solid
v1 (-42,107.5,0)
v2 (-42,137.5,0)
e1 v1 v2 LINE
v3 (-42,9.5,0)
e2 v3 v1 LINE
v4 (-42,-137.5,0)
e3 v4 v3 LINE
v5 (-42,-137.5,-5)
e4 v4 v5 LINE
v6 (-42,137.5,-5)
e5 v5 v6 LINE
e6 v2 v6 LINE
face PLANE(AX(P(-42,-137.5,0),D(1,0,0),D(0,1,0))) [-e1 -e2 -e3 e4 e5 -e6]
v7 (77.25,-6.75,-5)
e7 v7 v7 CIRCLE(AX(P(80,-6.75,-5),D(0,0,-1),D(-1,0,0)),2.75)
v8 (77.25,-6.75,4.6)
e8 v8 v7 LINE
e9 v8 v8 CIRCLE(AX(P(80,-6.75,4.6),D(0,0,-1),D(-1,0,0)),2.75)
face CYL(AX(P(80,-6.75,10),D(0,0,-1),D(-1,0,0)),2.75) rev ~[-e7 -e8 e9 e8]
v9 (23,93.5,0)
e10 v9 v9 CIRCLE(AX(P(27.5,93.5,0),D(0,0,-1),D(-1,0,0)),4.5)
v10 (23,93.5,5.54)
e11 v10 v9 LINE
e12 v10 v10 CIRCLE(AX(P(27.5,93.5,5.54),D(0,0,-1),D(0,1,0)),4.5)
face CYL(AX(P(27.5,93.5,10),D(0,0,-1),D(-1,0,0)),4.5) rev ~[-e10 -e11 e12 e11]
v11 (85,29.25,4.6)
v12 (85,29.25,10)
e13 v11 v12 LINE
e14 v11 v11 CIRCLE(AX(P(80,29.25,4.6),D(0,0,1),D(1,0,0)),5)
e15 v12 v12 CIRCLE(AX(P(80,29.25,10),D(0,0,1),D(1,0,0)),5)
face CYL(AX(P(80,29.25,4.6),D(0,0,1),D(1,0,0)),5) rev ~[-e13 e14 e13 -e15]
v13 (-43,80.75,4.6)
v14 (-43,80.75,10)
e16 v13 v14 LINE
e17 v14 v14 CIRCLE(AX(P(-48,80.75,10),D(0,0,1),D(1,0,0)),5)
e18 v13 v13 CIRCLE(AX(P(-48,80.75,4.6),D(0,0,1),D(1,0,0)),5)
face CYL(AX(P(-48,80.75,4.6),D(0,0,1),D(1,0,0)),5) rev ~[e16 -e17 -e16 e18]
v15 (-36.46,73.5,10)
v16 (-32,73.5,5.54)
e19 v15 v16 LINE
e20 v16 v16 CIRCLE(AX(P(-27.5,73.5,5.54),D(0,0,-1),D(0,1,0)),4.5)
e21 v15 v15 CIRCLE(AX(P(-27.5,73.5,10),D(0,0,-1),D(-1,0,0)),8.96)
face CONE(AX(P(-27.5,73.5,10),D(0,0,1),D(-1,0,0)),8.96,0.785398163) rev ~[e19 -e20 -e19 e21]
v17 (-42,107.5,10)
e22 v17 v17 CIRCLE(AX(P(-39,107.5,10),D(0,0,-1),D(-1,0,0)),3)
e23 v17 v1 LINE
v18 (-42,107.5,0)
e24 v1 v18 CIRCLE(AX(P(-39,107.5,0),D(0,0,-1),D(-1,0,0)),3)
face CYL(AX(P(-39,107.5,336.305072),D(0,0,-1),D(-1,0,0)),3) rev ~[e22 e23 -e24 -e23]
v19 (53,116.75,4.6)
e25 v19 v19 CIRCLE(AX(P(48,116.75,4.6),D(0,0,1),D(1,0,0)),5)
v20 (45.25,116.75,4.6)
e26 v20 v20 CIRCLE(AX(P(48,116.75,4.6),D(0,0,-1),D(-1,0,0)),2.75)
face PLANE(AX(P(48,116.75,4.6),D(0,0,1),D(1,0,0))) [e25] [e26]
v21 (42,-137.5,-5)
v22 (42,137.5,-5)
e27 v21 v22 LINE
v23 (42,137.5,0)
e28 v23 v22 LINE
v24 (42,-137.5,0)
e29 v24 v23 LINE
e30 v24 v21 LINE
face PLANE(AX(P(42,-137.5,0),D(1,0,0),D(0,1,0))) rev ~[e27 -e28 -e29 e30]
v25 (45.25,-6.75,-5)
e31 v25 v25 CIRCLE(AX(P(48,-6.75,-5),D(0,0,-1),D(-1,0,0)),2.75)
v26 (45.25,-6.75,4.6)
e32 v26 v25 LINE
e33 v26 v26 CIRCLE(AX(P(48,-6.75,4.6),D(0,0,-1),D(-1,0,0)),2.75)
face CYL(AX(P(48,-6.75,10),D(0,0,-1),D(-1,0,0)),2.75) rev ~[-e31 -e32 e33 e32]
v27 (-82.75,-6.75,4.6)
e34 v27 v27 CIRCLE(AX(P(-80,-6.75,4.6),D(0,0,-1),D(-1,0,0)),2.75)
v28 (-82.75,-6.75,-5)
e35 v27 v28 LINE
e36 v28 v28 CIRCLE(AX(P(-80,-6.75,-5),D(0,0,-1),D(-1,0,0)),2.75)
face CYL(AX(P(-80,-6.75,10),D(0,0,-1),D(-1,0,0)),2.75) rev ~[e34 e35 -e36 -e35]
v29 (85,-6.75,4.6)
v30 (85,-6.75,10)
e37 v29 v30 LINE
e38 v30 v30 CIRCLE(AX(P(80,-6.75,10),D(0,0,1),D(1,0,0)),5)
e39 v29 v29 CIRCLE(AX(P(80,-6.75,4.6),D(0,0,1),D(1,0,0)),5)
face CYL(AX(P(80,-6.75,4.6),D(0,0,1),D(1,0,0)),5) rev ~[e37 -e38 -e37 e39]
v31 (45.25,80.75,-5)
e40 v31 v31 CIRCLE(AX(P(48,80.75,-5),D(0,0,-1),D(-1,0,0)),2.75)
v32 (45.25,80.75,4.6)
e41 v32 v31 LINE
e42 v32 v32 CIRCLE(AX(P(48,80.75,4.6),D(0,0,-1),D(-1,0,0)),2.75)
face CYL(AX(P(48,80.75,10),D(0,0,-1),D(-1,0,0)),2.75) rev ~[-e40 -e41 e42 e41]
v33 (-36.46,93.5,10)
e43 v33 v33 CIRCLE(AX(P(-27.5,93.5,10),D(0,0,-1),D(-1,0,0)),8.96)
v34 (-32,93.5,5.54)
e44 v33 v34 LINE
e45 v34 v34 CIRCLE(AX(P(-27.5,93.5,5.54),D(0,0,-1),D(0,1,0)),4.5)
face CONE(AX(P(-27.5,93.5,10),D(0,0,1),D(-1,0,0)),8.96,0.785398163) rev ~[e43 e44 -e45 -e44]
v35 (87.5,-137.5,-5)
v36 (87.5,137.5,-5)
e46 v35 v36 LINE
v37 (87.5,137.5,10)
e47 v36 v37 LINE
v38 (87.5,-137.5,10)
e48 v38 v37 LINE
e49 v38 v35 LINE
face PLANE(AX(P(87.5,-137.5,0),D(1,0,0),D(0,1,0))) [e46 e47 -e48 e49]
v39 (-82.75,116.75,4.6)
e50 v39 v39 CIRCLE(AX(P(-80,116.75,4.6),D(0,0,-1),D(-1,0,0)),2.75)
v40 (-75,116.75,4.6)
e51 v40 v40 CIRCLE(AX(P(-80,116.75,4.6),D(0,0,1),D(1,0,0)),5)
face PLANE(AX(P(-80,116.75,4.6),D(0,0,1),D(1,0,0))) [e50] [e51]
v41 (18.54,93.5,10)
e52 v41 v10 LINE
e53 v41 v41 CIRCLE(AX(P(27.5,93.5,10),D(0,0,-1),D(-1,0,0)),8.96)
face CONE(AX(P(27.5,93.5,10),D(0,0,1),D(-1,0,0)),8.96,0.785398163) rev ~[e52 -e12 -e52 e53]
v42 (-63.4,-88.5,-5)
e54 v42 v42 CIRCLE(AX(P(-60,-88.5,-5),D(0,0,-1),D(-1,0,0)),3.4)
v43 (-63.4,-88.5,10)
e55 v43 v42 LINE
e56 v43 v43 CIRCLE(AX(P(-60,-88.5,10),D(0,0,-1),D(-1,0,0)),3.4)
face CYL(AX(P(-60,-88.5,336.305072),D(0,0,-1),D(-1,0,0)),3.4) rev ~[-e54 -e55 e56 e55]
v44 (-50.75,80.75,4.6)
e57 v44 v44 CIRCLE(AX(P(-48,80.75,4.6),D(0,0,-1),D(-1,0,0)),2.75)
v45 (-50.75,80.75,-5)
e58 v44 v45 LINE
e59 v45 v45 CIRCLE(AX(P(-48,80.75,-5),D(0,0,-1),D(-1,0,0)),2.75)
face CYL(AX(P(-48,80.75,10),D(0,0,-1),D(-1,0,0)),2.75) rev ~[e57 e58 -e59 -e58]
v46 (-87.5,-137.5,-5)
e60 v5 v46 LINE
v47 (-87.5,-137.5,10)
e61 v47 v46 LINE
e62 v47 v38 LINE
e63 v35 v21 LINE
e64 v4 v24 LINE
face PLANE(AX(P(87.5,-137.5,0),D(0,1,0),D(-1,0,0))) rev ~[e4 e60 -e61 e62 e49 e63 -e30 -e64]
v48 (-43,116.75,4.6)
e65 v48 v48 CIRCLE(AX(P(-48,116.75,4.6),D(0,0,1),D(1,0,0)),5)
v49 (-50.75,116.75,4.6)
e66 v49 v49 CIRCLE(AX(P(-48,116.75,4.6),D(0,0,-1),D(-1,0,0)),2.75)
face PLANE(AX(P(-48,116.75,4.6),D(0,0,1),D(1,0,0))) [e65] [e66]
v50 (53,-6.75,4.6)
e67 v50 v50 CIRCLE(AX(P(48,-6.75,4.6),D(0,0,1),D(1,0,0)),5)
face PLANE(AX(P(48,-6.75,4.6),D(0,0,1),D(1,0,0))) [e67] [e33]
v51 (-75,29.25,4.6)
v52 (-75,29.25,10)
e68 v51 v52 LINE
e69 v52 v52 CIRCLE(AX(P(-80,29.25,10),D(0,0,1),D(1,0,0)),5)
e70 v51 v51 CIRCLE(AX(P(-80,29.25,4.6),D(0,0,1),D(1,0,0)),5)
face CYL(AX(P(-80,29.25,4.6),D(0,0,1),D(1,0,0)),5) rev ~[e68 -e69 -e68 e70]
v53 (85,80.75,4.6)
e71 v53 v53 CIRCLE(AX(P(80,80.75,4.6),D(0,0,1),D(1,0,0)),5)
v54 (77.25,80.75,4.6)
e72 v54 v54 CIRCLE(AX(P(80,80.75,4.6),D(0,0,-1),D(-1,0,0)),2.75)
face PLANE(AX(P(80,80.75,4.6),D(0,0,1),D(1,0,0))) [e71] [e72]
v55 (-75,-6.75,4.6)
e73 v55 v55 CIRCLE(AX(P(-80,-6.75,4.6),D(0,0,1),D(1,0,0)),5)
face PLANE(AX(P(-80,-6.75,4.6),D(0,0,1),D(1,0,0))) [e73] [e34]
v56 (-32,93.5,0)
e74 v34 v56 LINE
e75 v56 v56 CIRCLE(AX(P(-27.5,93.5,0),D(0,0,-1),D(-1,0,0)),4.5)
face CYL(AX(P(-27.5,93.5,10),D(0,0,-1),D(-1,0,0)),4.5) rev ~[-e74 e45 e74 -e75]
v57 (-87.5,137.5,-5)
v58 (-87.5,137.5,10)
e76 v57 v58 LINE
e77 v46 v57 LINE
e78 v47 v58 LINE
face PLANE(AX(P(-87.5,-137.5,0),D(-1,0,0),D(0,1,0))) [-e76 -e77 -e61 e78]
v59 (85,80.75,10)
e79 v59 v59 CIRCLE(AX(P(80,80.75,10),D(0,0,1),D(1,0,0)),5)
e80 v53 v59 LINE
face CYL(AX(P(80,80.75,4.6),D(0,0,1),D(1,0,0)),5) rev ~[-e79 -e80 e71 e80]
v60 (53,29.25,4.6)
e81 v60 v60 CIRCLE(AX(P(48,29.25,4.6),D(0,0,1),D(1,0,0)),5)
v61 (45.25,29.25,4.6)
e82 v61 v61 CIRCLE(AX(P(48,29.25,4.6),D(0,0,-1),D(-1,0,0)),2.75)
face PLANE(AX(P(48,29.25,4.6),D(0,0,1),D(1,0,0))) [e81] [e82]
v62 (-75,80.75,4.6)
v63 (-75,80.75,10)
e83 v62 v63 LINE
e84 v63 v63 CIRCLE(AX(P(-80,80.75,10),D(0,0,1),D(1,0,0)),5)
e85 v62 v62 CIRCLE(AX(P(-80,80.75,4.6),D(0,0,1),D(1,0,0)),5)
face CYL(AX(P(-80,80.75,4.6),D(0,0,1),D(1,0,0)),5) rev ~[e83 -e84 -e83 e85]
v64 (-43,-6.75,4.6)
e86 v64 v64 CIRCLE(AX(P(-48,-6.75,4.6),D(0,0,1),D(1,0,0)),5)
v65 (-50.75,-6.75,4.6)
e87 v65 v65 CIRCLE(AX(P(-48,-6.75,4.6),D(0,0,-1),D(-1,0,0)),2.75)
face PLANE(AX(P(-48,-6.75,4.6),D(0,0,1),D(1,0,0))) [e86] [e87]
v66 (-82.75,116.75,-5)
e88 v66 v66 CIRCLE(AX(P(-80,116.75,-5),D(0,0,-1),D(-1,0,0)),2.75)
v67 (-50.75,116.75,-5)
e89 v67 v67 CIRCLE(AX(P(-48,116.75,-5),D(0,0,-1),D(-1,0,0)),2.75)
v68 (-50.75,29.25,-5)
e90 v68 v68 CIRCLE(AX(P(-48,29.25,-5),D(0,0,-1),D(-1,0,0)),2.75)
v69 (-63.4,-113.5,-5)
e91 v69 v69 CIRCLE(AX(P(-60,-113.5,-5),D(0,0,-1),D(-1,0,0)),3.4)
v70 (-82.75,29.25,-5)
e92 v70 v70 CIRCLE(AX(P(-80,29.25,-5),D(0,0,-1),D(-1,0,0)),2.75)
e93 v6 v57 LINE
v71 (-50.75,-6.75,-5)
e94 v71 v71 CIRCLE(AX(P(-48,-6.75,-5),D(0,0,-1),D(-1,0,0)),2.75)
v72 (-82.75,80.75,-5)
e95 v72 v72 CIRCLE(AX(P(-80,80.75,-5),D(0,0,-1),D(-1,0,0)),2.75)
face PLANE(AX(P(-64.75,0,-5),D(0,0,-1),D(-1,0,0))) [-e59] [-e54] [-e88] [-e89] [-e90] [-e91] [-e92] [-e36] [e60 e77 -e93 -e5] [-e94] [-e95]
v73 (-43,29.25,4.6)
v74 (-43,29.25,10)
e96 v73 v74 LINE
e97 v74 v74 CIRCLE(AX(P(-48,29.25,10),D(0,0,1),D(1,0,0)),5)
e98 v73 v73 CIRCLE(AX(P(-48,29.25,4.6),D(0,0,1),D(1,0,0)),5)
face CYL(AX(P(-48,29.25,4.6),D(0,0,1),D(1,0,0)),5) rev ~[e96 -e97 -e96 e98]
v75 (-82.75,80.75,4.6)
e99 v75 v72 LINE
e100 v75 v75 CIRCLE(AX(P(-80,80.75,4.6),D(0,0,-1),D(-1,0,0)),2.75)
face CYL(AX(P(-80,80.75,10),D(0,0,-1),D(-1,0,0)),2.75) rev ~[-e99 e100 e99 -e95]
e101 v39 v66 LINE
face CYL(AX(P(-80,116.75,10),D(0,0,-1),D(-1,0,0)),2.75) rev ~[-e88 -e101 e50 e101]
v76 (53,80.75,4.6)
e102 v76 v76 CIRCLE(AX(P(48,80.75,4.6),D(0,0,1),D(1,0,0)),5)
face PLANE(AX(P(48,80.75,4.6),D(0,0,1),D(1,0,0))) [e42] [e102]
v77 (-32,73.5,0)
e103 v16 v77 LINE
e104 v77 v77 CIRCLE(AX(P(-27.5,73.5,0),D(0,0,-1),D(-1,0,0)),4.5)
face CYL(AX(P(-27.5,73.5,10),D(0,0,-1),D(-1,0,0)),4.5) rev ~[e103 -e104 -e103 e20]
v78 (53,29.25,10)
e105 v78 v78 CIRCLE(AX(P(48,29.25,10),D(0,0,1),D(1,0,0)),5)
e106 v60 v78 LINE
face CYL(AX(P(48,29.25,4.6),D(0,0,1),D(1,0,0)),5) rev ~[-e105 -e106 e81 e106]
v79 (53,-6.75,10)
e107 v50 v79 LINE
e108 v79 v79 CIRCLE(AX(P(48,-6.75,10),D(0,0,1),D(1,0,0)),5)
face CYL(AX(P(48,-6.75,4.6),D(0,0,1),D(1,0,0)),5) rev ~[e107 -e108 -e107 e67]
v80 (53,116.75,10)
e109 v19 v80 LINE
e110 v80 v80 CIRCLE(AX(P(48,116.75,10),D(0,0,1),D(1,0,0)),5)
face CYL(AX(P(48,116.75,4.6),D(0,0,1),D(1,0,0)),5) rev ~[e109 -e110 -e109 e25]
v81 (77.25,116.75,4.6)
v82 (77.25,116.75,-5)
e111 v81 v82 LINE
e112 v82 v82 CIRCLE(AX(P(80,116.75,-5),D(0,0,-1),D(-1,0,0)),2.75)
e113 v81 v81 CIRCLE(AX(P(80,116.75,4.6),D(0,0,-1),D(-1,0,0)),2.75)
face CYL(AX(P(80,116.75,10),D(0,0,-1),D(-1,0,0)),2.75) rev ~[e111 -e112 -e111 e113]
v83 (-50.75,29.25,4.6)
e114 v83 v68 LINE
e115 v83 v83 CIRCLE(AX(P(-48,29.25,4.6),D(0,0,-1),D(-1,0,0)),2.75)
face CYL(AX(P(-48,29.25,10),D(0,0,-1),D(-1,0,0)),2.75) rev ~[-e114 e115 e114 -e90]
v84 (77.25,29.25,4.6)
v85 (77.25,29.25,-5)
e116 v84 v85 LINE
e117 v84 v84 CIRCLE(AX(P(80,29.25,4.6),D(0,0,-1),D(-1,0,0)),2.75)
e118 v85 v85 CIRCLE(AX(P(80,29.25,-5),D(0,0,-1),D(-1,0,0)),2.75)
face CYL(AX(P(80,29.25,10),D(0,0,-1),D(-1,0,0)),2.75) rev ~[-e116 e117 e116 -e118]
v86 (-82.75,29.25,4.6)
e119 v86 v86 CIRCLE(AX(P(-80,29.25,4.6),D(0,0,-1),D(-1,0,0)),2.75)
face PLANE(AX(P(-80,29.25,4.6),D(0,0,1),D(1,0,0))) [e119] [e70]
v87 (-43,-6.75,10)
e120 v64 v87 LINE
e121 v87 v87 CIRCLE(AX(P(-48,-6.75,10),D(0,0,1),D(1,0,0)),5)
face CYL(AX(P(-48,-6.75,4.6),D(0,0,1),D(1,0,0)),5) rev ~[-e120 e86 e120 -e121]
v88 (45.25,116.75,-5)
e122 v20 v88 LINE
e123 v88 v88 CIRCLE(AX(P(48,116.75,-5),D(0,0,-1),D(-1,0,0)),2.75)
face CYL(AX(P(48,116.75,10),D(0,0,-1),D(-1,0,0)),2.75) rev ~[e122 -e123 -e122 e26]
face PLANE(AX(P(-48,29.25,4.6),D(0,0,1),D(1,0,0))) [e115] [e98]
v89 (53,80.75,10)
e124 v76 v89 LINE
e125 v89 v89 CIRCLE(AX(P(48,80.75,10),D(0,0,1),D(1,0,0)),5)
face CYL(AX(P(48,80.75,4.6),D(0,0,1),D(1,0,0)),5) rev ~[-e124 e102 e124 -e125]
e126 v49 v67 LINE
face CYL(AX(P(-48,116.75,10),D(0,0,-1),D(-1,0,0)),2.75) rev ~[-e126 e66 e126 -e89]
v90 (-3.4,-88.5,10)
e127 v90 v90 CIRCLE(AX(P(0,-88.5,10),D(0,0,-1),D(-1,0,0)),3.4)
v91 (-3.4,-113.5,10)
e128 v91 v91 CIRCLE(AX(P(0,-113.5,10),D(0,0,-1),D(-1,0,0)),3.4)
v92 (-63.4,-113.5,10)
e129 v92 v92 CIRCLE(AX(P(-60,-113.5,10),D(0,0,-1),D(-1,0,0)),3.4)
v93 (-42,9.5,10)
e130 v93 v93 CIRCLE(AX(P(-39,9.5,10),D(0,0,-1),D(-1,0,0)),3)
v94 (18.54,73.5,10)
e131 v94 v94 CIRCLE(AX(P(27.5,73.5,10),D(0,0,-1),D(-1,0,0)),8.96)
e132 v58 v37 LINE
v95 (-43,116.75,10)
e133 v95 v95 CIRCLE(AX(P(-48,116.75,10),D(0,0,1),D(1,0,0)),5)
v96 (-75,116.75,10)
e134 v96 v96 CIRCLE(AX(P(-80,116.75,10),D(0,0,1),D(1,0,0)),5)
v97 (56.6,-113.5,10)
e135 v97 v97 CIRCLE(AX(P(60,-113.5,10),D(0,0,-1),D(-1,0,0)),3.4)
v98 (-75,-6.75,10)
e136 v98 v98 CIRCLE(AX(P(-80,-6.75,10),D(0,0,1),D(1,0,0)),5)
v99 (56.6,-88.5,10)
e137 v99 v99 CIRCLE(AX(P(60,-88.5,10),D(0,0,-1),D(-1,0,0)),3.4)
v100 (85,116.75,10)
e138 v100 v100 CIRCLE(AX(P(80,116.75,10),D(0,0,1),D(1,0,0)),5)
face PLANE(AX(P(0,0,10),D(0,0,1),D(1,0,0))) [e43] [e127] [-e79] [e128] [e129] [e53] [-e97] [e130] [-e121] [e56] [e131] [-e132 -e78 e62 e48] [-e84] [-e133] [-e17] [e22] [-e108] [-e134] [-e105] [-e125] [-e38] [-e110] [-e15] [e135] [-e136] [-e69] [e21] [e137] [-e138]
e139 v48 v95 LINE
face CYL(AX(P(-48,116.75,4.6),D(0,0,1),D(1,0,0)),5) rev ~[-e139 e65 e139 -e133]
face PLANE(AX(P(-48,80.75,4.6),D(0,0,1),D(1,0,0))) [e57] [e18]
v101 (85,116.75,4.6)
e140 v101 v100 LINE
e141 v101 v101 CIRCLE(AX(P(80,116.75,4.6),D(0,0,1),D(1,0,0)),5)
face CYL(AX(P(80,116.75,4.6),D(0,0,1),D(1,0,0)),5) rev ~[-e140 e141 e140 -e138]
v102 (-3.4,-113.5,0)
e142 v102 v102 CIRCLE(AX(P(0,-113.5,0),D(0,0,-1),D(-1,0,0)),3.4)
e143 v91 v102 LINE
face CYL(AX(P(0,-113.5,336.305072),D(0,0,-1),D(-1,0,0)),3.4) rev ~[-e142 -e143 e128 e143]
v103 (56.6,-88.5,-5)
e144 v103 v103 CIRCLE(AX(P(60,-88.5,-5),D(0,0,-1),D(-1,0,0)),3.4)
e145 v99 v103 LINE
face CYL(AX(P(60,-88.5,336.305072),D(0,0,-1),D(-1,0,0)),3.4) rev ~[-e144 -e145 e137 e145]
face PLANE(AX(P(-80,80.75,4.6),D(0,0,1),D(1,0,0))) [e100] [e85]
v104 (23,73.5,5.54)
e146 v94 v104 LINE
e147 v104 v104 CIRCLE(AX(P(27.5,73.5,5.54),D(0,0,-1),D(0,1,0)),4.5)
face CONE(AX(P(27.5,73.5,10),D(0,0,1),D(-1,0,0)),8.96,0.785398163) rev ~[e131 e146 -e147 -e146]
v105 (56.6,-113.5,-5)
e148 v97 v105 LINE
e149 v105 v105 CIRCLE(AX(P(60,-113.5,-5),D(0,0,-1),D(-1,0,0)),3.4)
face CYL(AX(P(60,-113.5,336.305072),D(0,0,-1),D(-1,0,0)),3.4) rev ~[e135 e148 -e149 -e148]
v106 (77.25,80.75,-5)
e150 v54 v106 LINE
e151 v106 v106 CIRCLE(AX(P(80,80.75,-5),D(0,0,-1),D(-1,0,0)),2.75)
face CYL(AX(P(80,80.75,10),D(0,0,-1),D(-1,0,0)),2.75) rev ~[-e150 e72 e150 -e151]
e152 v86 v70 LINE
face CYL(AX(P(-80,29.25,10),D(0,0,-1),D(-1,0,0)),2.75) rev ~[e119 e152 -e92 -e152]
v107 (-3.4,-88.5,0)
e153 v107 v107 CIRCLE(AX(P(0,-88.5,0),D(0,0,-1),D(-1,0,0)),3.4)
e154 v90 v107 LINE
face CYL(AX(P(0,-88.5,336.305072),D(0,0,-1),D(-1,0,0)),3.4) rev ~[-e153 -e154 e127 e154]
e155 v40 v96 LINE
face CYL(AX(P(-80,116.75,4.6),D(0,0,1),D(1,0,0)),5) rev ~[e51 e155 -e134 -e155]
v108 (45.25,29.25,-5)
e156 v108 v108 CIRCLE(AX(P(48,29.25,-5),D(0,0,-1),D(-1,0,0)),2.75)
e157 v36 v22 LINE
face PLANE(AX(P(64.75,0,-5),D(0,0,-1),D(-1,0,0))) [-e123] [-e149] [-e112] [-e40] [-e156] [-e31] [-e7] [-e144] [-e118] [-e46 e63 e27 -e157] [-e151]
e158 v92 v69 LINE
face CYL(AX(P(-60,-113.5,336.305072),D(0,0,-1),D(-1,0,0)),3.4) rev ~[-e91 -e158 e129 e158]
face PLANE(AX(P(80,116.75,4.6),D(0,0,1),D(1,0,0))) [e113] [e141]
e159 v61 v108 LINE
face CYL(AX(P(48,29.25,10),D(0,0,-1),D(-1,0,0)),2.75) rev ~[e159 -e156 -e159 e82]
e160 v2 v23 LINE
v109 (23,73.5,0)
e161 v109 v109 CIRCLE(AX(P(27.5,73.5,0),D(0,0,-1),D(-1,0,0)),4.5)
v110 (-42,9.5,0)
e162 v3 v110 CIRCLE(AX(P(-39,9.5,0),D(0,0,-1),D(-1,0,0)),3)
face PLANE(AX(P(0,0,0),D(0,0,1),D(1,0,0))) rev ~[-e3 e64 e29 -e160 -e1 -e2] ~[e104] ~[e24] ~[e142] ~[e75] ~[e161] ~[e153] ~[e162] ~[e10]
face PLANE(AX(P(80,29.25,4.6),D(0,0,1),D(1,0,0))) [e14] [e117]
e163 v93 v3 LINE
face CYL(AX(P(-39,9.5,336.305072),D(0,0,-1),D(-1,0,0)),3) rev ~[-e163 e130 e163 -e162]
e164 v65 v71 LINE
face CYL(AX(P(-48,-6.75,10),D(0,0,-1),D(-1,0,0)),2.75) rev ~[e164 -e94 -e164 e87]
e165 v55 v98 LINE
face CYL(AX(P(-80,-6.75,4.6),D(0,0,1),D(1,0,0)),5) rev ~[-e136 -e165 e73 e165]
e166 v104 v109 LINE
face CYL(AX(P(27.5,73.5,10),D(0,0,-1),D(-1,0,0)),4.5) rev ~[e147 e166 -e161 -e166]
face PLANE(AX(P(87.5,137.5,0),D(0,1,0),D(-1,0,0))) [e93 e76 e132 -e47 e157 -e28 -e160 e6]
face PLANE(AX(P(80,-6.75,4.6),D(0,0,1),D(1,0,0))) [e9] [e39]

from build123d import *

# Parameters (mm, degrees)
SKETCH_1_W                   = 175
SKETCH_1_H                   = 275
EXTRUDE_1_DEPTH              = 10
SKETCH_10_W                  = 45.5
SKETCH_10_H                  = 275
EXTRUDE_2_DEPTH              = 5
HOLE_WIZARD_M8_1_D           = 9
HOLE_WIZARD_M8_1_CSINK_D     = 17.92
HOLE_WIZARD_M8_1_CSINK_ANGLE = 90
HOLE_WIZARD_M8_1_2_D         = 6.8
HOLE_WIZARD_M5_1_D           = 5.5
HOLE_WIZARD_M5_1_CBORE_D     = 10
HOLE_WIZARD_M5_1_CBORE_DEPTH = 5.4
F_6_0MM_1_D                  = 6


with BuildPart() as part:
    # 草图1 → 凸台-拉伸1 (new body)
    with BuildSketch(Plane.XY):
        Rectangle(SKETCH_1_W, SKETCH_1_H)
    extrude(amount=EXTRUDE_1_DEPTH)

    # 草图10 → 凸台-拉伸2 (add)
    with BuildSketch(Plane(origin=(0, 0, 0), x_dir=(-1, 0, 0), z_dir=(0, 0, -1))):
        with Locations((-64.75, 0)):
            Rectangle(SKETCH_10_W, SKETCH_10_H)
        with Locations((64.75, 0)):
            Rectangle(SKETCH_10_W, SKETCH_10_H)
    extrude(amount=EXTRUDE_2_DEPTH)

    # Hole Wizard M8 _1 (through all)
    with Locations(Plane.XY.offset(10)):
        with Locations((-27.5, 93.5), (-27.5, 73.5), (27.5, 93.5), (27.5, 73.5)):
            CounterSinkHole(HOLE_WIZARD_M8_1_D / 2, HOLE_WIZARD_M8_1_CSINK_D / 2, counter_sink_angle=HOLE_WIZARD_M8_1_CSINK_ANGLE)

    # Hole Wizard M8 _1 2 (through all)
    with Locations(Plane.XY.offset(10)):
        with Locations((0, -113.5), (-60, -113.5), (60, -113.5), (0, -88.5), (-60, -88.5), (60, -88.5)):
            Hole(HOLE_WIZARD_M8_1_2_D / 2)

    # M5 六角凹头螺钉的柱形沉头孔1 (through all)
    with Locations(Plane.XY.offset(10)):
        with Locations((-80, 116.75), (-48, 116.75), (-80, 80.75), (-48, 80.75), (-80, 29.25), (-48, 29.25), (-80, -6.75), (-48, -6.75), (48, -6.75), (80, -6.75), (48, 29.25), (80, 29.25), (48, 80.75), (80, 80.75), (48, 116.75), (80, 116.75)):
            CounterBoreHole(HOLE_WIZARD_M5_1_D / 2, HOLE_WIZARD_M5_1_CBORE_D / 2, HOLE_WIZARD_M5_1_CBORE_DEPTH)

    # Ø6.0mm 暗销孔1 (through all)
    with Locations(Plane.XY.offset(10)):
        with Locations((-39, 107.5), (-39, 9.5)):
            Hole(F_6_0MM_1_D / 2)


solid = part.part
